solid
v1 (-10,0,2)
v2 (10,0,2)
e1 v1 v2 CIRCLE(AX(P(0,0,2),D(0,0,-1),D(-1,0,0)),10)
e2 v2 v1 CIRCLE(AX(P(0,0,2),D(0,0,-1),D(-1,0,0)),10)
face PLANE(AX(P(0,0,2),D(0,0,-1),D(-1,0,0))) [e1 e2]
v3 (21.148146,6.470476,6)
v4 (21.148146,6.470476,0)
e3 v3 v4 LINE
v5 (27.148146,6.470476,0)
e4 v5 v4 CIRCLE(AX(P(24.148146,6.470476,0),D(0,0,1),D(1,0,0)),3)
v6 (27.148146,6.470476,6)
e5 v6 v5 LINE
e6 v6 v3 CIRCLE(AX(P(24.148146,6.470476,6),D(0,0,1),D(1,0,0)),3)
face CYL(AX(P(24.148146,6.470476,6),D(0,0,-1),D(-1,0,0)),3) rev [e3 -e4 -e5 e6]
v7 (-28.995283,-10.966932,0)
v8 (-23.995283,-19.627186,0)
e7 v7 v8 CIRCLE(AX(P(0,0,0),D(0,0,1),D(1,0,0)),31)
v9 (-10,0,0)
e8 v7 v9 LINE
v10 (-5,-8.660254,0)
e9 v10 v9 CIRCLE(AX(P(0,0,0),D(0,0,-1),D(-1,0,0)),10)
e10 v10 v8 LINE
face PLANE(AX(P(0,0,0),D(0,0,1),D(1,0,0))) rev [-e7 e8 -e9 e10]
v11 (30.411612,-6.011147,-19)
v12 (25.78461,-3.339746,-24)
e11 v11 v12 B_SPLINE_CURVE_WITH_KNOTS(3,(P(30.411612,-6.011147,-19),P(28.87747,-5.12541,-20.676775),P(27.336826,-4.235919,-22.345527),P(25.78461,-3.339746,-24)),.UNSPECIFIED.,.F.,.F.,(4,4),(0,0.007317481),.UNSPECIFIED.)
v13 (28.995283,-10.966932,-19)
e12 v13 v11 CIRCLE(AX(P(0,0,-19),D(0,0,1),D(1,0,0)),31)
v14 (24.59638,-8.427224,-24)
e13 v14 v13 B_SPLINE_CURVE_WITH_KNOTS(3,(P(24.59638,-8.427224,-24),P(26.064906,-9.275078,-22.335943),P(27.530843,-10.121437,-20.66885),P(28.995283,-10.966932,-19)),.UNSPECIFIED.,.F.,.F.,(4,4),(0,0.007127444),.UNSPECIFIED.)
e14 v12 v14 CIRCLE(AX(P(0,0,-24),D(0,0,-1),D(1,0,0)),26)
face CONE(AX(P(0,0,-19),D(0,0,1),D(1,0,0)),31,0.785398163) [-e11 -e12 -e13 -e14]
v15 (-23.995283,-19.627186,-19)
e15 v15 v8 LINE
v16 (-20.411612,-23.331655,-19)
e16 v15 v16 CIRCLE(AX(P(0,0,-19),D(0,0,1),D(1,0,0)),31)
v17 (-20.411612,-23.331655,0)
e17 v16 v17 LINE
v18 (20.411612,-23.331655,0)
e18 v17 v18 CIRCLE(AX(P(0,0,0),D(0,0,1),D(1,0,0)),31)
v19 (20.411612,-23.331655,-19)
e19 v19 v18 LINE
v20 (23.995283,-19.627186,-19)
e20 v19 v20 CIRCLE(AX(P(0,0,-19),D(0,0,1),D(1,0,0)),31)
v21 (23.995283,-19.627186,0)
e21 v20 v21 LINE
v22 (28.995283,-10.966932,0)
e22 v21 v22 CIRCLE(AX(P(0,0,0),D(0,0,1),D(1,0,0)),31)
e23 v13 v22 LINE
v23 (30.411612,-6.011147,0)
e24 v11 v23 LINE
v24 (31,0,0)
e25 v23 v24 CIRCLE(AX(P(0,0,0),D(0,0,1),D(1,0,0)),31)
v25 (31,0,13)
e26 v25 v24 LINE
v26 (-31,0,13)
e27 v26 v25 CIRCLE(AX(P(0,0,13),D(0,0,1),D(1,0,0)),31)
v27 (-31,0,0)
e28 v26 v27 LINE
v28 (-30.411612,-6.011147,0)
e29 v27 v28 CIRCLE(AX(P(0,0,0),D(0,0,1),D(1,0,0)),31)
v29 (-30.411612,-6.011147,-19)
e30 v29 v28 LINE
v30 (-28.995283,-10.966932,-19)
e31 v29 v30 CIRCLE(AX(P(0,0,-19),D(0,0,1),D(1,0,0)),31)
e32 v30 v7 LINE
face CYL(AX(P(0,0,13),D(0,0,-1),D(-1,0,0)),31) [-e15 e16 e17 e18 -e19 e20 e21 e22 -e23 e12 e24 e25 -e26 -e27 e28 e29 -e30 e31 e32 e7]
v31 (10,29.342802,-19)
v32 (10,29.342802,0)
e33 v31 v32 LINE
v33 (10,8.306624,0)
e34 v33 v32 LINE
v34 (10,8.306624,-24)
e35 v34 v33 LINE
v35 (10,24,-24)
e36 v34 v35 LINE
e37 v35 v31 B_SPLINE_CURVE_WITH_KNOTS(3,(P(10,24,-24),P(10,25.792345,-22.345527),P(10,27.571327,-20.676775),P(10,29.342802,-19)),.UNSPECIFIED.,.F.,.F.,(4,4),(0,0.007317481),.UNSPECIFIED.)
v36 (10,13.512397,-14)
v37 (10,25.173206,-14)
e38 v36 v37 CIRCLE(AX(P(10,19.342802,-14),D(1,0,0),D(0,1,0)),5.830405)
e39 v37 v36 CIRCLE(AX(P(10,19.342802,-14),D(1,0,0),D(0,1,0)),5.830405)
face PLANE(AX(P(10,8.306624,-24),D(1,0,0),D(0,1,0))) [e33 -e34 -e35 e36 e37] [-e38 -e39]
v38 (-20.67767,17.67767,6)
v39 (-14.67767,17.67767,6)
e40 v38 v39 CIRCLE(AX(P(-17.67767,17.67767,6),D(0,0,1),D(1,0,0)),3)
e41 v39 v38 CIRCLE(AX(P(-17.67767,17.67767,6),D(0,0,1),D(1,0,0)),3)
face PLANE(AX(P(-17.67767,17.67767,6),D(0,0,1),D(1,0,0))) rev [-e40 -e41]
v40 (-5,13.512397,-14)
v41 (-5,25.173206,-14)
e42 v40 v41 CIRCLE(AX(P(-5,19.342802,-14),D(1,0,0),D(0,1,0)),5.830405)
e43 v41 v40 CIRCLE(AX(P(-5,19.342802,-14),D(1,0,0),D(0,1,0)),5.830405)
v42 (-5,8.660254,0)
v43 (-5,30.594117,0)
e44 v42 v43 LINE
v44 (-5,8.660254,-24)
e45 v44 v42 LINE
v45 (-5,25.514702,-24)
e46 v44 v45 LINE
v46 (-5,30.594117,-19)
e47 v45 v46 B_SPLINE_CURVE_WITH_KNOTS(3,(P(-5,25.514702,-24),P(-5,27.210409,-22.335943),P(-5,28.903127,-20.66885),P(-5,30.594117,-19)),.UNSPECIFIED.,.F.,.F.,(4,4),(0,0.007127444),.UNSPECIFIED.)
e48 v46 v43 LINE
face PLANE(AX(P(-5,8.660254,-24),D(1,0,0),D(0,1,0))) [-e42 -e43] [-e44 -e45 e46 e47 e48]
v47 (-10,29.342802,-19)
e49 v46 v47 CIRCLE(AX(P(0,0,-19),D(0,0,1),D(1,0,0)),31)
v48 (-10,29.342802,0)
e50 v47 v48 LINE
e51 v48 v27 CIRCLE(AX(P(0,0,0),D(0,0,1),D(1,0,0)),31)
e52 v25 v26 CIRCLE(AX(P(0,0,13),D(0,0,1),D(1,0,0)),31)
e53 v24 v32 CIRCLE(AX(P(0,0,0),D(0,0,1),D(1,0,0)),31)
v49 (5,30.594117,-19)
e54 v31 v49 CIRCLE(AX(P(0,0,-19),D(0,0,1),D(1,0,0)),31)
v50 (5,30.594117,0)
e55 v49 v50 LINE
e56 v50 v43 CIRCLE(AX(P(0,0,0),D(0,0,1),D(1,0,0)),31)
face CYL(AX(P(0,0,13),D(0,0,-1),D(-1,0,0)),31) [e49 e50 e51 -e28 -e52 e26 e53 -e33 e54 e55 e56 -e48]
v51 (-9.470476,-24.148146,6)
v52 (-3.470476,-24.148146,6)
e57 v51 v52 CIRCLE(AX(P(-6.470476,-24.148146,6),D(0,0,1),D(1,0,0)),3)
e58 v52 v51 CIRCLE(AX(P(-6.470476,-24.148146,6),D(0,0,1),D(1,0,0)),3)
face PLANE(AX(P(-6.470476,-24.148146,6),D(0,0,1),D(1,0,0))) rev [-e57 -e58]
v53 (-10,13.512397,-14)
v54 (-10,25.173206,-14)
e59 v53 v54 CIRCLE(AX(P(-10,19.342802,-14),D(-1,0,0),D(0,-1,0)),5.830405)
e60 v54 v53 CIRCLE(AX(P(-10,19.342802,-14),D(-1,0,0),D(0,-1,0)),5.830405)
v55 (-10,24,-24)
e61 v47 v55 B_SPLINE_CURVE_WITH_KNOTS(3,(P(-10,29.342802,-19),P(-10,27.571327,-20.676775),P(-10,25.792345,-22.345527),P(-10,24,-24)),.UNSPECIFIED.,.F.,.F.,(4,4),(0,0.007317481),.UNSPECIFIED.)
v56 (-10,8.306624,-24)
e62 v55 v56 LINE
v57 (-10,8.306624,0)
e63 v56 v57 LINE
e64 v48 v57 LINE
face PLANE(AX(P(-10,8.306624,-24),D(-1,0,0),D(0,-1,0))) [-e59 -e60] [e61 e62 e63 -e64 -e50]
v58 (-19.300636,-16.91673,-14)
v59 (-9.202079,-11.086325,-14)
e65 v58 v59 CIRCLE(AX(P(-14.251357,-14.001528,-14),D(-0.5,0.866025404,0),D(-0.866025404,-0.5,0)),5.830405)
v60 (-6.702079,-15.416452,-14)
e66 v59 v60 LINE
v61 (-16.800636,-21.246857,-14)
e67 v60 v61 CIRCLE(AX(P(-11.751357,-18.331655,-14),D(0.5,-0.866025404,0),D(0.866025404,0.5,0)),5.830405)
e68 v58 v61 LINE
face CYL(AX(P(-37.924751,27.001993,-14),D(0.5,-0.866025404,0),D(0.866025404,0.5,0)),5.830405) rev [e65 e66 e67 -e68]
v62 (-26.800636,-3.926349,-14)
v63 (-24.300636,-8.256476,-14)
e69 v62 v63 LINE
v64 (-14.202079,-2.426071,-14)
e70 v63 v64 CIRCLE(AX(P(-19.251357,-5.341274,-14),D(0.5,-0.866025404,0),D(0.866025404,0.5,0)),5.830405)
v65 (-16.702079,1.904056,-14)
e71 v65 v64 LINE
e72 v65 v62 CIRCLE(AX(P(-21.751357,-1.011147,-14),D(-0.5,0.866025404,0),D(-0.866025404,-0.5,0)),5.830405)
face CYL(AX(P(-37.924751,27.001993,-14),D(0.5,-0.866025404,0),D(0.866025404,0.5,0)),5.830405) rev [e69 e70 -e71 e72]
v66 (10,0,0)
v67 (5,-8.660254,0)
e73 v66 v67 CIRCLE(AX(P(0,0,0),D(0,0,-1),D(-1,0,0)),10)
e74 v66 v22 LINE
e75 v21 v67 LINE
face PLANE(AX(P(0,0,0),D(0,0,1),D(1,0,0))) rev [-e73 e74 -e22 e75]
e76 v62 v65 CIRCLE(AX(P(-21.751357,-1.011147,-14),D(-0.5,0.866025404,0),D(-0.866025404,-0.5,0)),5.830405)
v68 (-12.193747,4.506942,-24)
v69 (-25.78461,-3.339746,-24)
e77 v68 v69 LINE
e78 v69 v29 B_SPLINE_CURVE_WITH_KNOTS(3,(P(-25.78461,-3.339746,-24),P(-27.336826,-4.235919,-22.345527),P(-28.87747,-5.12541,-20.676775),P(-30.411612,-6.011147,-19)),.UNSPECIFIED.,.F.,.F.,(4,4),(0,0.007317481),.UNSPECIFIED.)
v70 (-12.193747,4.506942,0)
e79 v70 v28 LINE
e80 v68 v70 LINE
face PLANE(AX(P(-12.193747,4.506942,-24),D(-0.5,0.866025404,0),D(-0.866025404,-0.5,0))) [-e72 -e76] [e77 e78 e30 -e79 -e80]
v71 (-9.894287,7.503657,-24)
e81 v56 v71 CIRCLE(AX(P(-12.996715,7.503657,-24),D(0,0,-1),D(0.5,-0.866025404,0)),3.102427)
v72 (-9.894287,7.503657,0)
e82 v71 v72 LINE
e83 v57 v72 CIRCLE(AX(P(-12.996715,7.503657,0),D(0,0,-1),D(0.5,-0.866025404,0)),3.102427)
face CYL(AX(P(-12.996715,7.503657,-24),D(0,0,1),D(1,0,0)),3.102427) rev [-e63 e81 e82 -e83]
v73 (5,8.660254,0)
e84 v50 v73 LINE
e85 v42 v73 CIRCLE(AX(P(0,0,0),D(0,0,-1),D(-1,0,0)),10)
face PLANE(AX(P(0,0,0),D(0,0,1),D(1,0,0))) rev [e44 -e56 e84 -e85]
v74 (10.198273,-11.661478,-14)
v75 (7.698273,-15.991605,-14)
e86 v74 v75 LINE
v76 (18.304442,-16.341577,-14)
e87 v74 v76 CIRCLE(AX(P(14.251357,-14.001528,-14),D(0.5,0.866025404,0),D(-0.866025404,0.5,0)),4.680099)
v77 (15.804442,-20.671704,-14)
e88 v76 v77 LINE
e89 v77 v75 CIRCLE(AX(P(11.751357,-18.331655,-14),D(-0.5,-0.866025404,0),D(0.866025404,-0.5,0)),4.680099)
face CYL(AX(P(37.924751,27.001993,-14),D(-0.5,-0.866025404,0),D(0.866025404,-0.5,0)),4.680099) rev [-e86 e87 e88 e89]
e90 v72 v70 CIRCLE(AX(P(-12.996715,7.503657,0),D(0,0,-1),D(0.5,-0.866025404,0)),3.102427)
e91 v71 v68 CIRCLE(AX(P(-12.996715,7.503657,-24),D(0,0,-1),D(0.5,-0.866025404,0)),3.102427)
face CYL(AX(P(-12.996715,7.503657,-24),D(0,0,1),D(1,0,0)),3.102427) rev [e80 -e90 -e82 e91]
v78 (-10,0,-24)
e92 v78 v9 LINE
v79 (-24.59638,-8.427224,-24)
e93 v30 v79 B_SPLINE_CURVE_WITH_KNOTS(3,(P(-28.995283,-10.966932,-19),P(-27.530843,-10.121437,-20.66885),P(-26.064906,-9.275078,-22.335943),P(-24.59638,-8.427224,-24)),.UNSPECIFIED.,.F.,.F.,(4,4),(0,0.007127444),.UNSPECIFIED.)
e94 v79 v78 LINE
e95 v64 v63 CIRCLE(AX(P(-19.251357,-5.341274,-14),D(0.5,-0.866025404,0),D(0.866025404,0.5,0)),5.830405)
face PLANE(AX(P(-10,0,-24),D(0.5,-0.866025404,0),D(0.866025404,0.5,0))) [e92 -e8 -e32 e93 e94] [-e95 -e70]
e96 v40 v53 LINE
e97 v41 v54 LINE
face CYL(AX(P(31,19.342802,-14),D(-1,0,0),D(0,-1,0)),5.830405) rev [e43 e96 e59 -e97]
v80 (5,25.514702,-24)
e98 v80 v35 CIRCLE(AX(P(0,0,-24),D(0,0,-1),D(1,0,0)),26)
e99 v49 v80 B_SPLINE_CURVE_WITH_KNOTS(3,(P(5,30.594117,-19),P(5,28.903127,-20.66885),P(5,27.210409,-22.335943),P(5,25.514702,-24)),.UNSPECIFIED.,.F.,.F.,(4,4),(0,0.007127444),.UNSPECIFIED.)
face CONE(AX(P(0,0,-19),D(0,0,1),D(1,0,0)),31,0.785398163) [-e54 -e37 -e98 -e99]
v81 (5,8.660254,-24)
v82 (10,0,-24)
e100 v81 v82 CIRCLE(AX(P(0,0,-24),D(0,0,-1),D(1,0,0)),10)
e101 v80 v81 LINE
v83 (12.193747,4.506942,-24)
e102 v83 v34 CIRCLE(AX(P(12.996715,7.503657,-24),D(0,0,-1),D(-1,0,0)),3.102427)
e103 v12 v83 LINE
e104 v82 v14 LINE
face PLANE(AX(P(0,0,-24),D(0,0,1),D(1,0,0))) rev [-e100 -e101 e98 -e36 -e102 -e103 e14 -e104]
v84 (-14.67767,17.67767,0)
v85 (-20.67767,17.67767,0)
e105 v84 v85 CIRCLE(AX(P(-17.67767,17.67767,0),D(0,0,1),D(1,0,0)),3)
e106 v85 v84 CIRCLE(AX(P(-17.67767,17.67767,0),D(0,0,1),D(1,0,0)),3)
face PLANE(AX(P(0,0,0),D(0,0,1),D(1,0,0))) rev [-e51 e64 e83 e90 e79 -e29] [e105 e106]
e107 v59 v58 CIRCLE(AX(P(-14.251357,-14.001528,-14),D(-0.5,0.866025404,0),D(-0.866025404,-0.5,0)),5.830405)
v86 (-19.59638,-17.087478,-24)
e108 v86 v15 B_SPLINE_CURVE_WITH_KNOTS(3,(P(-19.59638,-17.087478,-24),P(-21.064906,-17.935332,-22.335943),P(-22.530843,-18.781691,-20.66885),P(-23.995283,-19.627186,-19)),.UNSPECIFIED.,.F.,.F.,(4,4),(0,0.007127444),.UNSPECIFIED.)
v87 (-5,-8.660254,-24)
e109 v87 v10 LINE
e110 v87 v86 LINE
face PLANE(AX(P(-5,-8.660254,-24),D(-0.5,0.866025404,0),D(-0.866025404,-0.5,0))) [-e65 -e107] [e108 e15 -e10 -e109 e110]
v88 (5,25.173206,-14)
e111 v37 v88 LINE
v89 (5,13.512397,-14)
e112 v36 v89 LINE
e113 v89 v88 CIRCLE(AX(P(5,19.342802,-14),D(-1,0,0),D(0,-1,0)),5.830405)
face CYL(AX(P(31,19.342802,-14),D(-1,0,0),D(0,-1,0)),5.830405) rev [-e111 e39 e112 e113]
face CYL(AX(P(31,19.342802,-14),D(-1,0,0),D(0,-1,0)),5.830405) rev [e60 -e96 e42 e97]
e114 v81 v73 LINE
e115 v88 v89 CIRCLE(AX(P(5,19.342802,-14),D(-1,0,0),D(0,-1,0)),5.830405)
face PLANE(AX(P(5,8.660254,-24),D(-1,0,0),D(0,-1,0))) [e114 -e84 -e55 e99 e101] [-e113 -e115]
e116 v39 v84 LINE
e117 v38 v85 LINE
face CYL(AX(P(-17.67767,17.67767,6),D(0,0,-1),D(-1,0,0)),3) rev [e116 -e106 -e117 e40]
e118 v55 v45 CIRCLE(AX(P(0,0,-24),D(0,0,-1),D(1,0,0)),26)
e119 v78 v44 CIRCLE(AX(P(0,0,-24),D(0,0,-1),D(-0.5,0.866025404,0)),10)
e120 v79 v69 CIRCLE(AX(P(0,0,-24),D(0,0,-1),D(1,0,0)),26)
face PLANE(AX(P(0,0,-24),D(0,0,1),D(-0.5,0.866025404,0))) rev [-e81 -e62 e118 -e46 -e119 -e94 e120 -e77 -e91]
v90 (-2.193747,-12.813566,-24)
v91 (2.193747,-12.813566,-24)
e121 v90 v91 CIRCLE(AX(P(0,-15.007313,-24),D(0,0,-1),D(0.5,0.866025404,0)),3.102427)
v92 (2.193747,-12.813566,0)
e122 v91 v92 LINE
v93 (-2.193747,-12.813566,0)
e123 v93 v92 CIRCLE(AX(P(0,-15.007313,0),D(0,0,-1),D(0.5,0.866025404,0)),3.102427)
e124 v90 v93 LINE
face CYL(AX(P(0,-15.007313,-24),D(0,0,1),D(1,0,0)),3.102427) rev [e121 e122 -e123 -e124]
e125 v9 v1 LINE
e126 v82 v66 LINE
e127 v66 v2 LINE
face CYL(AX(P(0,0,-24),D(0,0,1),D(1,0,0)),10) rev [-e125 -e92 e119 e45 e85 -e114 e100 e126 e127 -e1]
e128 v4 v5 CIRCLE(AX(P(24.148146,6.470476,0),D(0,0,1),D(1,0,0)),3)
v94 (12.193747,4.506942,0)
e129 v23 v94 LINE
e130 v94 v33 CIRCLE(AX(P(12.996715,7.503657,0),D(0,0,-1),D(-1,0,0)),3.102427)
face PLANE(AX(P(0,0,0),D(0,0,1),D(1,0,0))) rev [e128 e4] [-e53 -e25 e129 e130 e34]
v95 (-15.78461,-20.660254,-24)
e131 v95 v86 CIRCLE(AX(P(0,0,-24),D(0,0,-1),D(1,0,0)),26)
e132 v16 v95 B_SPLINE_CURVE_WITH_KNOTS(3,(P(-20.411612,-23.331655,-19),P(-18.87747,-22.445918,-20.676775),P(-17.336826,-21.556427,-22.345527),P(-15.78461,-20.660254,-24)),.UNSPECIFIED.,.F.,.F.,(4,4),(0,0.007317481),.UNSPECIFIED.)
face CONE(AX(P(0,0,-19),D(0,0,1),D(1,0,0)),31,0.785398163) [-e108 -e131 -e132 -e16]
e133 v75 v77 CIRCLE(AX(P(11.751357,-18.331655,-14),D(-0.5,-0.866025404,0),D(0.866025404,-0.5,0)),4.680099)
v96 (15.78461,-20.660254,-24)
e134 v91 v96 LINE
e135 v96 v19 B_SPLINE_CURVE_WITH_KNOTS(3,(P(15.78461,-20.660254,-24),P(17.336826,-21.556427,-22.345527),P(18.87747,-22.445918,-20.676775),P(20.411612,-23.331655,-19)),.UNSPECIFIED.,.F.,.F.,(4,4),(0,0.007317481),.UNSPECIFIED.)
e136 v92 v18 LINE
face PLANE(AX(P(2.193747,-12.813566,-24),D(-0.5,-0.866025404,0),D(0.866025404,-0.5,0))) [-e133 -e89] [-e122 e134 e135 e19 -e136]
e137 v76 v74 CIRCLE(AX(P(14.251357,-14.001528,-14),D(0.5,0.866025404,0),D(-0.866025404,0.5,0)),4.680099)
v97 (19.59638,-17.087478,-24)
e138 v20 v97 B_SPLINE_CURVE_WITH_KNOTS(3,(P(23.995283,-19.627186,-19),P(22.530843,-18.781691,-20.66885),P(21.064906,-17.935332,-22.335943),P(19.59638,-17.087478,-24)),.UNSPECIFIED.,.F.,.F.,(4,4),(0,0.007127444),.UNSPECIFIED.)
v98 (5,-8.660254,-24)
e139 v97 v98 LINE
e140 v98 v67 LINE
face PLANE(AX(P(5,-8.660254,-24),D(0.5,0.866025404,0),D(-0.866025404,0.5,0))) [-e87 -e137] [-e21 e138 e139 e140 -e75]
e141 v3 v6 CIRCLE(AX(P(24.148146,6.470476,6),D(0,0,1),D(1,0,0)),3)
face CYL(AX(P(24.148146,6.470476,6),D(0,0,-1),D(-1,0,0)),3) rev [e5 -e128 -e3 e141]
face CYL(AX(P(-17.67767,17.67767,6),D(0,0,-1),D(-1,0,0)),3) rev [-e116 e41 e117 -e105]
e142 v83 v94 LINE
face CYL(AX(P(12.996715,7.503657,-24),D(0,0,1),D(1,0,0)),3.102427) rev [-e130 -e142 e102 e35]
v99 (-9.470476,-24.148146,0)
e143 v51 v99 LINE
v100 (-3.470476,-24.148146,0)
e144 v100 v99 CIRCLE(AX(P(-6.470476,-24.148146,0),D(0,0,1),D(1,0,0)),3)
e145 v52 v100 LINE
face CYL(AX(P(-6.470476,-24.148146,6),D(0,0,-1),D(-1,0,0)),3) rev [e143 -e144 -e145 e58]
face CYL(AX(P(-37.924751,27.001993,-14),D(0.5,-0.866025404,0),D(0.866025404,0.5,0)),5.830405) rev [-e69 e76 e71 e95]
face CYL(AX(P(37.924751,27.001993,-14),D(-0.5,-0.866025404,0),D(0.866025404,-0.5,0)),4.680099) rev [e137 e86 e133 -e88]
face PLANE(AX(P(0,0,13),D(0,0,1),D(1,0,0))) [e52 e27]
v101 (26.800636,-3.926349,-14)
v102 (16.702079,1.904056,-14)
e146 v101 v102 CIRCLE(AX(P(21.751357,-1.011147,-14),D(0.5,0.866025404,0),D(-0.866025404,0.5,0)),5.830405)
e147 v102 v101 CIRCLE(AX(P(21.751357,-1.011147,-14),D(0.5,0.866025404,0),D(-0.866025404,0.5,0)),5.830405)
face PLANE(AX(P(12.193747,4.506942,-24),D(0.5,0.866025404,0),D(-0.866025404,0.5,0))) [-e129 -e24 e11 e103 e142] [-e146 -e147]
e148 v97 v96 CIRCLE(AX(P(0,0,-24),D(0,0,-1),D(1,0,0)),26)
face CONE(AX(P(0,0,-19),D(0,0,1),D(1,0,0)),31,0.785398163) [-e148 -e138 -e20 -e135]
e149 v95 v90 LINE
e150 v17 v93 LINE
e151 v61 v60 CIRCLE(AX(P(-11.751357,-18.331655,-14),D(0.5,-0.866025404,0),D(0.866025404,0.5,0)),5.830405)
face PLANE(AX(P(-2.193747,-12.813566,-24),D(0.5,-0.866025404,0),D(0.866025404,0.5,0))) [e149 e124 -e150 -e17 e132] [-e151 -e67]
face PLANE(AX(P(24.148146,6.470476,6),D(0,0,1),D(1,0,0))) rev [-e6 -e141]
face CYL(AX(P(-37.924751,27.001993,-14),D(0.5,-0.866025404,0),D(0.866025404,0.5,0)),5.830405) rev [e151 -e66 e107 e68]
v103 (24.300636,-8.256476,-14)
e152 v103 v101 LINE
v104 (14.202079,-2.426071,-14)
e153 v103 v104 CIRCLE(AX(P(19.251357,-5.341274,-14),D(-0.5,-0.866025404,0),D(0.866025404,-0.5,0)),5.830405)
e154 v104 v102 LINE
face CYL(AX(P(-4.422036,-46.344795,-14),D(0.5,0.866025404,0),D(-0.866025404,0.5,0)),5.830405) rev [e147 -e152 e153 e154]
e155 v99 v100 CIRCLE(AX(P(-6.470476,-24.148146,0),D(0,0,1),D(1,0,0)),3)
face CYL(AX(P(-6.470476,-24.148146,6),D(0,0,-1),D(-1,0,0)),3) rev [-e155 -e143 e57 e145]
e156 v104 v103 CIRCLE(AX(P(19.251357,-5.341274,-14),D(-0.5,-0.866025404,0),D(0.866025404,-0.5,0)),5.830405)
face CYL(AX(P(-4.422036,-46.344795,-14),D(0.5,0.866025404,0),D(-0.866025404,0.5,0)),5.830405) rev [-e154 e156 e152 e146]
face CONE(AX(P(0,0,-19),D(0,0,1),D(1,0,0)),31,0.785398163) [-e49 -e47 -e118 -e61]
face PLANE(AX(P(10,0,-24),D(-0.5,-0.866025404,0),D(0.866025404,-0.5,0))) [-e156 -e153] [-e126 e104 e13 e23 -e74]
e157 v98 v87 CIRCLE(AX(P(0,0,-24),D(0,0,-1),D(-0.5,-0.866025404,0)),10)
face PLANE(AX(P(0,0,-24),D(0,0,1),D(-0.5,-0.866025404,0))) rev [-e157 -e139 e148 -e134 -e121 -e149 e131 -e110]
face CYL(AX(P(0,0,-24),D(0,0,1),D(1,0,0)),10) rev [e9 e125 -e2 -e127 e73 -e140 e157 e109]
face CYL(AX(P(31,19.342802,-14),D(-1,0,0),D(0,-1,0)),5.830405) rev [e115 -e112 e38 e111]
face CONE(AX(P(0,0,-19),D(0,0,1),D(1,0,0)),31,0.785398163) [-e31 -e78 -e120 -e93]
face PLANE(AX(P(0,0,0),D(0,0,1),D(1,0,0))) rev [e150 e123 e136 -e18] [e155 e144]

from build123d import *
from build123d.topology import SkipClean

# Parameters (mm, degrees)
BASE_DISC_SKETCH_R         = 31
BASE_DISC_DEPTH            = 13
BASE_SLOT_SKETCH_3X_R      = 3
BASE_SLOTS_3X_DEPTH        = 6
CLAMP_START                = -24
CLAMP_LUG_DEPTH            = 24
LUG_HOLE_A_SKETCH_R        = 4.680098696
LUG_HOLE_A_DEPTH           = 57.727418415
LUG_HOLE_B_SKETCH_R        = 5.830404683
LUG_HOLE_B_DEPTH           = 59.693575035
CLAMP_LUG_PATTERN_3X_COUNT = 3
FACE_RECESS_SKETCH_R       = 10
FACE_RECESS_2MM_DEPTH      = 2
LUG_CHAMFER_5MM_SIZE       = 5


with BuildPart() as part:
    # Base Disc Sketch → Base Disc (new body)
    with BuildSketch(Plane.XY):
        with Locations(Location((0, 0, 0), (0, 0, 180))):
            Circle(BASE_DISC_SKETCH_R)
    extrude(amount=BASE_DISC_DEPTH)

    # Base Slot Sketch 3x → Base Slots 3x (cut)
    with BuildSketch(Plane.XY):
        with Locations((-6.470476128, -24.148145657)):
            Circle(BASE_SLOT_SKETCH_3X_R)
        with Locations((-17.67766953, 17.67766953)):
            Circle(BASE_SLOT_SKETCH_3X_R)
        with Locations((24.148145657, 6.470476128)):
            Circle(BASE_SLOT_SKETCH_3X_R)
    extrude(amount=BASE_SLOTS_3X_DEPTH, mode=Mode.SUBTRACT)

    # Clamp Lug Sketch → Clamp Lug (add)
    with SkipClean():  # the faces are left unmerged after this step: merging them gives an invalid solid
        with BuildSketch(Plane.XY.offset(CLAMP_START)):
            with BuildLine():
                Line((5, 8.660254038), (5, 30.594117082))
                ThreePointArc((5, 30.594117082), (7.526051267, 30.072554802), (10, 29.342801502))
                Line((10, 29.342801502), (10, 8.306623863))
                ThreePointArc((10, 8.306623863), (10.309933784, 5.952443046), (12.193747285, 4.506942106))
                Line((12.193747285, 4.506942106), (30.411611519, -6.011146713))
                ThreePointArc((30.411611519, -6.011146713), (29.806622049, -8.518525814), (28.995282599, -10.966931522))
                Line((28.995282599, -10.966931522), (10, 0))
                ThreePointArc((10, 0), (8.660254038, 5), (5, 8.660254038))
            make_face()
        clamp_lug = extrude(amount=CLAMP_LUG_DEPTH)

    # Lug Hole A Sketch → Lug Hole A (cut, through all)
    with SkipClean():  # the faces are left unmerged after this step: merging them gives an invalid solid
        with BuildSketch(Plane(origin=(10, 0, 0), x_dir=(0, 0, -1), z_dir=(1, 0, 0))):
            with Locations(Location((14, 19.342801502, 0), (0, 0, 90))):
                Circle(LUG_HOLE_A_SKETCH_R)
        lug_hole_a = extrude(amount=-LUG_HOLE_A_DEPTH, mode=Mode.SUBTRACT)

    # Lug Hole B Sketch → Lug Hole B (cut, through all)
    with SkipClean():  # the faces are left unmerged after this step: merging them gives an invalid solid
        with BuildSketch(Plane(origin=(5, 8.660254038, 0), x_dir=(0.8660254037844388, -0.4999999999999998, 0), z_dir=(0.4999999999999998, 0.8660254037844388, 0))):
            with Locations(Location((19.342801502, 14, 0), (0, 0, 180))):
                Circle(LUG_HOLE_B_SKETCH_R)
        lug_hole_b = extrude(amount=-LUG_HOLE_B_DEPTH, mode=Mode.SUBTRACT)

    # Clamp Lug Pattern 3x: Clamp Lug, Lug Hole A, Lug Hole B ×3 about axis
    with SkipClean():  # the faces are left unmerged after this step: merging them gives an invalid solid
        clamp_lug_pattern_3x_axis = Axis((0, 0, 0), (0, 0, 1))
        add([clamp_lug.rotate(clamp_lug_pattern_3x_axis, i * 360 / CLAMP_LUG_PATTERN_3X_COUNT) for i in range(1, CLAMP_LUG_PATTERN_3X_COUNT)])
        add([lug_hole_a.rotate(clamp_lug_pattern_3x_axis, i * 360 / CLAMP_LUG_PATTERN_3X_COUNT) for i in range(1, CLAMP_LUG_PATTERN_3X_COUNT)], mode=Mode.SUBTRACT)
        add([lug_hole_b.rotate(clamp_lug_pattern_3x_axis, i * 360 / CLAMP_LUG_PATTERN_3X_COUNT) for i in range(1, CLAMP_LUG_PATTERN_3X_COUNT)], mode=Mode.SUBTRACT)

    # Face Recess Sketch → Face Recess 2mm (cut)
    with SkipClean():  # the faces are left unmerged after this step: merging them gives an invalid solid
        with BuildSketch(Plane(origin=(0, 0, 0), x_dir=(-1, 0, 0), z_dir=(0, 0, -1))):
            Circle(FACE_RECESS_SKETCH_R)
        extrude(amount=-FACE_RECESS_2MM_DEPTH, mode=Mode.SUBTRACT)

    # Lug Chamfer 5mm
    lug_chamfer_5mm_edges = [part.edges().sort_by_distance(p)[0] for p in [
        (7.526051267, 30.072554802, -24),
        (29.806622049, -8.518525814, -24),
        (-29.806622049, -8.518525814, -24),
        (-7.526051267, 30.072554802, -24),
        (22.280570782, -21.554028988, -24),
        (-22.280570782, -21.554028988, -24),
    ]]
    chamfer(lug_chamfer_5mm_edges, length=LUG_CHAMFER_5MM_SIZE)


solid = part.part
